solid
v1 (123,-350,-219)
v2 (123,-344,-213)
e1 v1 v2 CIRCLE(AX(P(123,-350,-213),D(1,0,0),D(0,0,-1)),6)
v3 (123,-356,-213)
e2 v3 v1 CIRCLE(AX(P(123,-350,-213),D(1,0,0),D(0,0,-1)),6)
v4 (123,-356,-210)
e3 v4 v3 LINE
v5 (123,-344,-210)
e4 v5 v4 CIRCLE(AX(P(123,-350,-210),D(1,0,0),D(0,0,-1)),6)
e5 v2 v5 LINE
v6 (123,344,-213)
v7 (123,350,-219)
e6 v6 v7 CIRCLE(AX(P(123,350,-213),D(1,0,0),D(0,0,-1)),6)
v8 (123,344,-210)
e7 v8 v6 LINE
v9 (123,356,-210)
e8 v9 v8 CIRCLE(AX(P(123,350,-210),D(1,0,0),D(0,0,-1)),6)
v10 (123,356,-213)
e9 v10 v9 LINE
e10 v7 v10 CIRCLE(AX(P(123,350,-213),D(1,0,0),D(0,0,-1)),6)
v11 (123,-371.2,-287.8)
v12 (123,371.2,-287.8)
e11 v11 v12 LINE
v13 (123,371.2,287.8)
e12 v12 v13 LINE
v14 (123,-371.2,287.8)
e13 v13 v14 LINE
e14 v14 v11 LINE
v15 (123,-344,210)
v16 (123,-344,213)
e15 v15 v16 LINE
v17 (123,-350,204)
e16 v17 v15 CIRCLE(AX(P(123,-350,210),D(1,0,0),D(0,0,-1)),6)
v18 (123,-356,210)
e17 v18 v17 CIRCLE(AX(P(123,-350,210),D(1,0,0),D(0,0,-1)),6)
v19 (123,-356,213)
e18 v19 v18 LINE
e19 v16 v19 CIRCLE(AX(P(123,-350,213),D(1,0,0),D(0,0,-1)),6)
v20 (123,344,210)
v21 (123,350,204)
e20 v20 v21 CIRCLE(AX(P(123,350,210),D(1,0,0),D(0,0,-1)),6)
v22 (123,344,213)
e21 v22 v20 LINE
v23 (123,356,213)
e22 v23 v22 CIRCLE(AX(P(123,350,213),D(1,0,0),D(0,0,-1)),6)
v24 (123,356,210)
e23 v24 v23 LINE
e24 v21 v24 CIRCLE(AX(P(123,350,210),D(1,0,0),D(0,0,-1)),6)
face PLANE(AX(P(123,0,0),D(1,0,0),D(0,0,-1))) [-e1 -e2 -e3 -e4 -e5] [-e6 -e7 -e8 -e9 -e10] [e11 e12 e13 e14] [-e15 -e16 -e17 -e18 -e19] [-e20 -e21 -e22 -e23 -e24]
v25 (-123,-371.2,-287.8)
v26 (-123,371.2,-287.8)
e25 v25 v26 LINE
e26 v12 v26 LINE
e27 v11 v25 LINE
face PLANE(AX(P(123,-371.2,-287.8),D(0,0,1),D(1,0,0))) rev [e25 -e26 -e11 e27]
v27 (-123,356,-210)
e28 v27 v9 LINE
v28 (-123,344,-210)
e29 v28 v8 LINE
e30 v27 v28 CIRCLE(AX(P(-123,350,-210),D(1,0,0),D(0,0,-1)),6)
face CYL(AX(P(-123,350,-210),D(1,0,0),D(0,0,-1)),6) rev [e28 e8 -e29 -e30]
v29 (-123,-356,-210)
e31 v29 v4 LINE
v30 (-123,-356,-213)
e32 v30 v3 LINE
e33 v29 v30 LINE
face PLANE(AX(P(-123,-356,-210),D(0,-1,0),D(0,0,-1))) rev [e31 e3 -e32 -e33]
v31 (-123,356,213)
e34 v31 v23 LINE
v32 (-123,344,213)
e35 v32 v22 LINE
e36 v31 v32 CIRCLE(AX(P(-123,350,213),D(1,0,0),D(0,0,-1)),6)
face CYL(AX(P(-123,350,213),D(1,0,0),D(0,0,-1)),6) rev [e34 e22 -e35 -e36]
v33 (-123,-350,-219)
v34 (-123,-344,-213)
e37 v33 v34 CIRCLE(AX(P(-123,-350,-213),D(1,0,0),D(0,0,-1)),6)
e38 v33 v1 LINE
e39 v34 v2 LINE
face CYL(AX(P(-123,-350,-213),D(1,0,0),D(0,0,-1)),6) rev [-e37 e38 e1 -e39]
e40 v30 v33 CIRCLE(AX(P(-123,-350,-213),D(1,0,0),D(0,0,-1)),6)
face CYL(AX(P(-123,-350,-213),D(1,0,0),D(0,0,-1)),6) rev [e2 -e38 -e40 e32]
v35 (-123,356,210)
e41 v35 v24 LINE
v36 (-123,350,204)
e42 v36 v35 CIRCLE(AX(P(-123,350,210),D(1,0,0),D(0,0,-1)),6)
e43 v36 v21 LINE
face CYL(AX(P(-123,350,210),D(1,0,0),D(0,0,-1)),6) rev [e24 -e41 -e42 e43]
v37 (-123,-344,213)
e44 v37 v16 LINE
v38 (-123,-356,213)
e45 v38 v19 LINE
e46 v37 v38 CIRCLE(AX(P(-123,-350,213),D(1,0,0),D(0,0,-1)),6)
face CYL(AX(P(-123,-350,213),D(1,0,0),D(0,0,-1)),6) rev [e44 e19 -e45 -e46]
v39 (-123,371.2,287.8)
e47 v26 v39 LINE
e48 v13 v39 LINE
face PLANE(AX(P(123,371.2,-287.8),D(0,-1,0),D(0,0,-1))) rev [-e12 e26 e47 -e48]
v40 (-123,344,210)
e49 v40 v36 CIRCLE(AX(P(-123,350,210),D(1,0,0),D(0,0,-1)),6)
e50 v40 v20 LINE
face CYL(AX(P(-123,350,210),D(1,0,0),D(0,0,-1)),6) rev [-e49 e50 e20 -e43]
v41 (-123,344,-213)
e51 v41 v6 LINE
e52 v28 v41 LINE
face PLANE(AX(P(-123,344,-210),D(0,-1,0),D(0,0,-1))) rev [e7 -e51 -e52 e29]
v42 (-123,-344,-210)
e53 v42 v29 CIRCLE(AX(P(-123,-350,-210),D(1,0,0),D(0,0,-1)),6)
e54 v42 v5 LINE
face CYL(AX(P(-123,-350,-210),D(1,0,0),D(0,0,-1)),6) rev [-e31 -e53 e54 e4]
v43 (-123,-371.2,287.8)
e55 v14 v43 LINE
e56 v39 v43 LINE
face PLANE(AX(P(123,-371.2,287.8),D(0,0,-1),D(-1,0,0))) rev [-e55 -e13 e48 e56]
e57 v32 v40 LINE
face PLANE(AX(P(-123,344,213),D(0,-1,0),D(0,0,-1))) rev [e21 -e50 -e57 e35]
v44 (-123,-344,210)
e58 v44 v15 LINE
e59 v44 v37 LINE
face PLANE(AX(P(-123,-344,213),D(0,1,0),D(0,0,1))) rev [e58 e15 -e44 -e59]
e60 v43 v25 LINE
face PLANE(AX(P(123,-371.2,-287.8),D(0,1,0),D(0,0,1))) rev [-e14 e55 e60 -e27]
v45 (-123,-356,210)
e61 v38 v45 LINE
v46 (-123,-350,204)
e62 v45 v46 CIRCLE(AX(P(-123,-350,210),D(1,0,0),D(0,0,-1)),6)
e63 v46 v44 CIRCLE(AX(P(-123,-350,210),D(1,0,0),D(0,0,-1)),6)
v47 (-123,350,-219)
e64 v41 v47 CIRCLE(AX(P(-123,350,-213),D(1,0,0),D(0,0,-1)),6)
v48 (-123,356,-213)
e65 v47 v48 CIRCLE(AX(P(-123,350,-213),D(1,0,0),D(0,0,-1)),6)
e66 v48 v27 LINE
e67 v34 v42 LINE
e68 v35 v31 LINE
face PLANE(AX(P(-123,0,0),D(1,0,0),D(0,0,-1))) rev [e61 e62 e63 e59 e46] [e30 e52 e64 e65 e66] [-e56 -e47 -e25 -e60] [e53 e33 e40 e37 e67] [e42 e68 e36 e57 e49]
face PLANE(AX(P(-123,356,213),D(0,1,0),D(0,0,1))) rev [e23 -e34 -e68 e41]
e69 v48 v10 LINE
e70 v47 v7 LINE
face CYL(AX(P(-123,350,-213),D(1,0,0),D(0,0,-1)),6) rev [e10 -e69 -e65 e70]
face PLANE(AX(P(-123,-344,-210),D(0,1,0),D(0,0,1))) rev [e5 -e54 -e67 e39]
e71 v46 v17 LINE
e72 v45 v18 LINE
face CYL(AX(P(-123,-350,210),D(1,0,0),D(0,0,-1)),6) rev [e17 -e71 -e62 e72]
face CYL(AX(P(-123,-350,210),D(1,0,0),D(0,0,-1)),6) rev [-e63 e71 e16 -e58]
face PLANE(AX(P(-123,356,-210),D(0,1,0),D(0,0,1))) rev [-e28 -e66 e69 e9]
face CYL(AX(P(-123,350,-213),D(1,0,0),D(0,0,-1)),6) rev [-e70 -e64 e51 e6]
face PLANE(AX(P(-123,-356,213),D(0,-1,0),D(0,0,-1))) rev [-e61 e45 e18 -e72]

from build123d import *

# Parameters (mm, degrees)
SKETCH_1_W          = 575.6
SKETCH_1_H          = 742.4
EXTRUDE_1_DEPTH     = 123
CUT_EXTRUDE_1_DEPTH = 531.220972803


with BuildPart() as part:
    # 草图1 → 凸台-拉伸1 (new, symmetric)
    with BuildSketch(Plane(origin=(0, 0, 0), x_dir=(0, 0, -1), z_dir=(1, 0, 0))):
        Rectangle(SKETCH_1_W, SKETCH_1_H)
    extrude(amount=EXTRUDE_1_DEPTH, both=True)

    # 草图2 → 切除-拉伸1 (cut, through all)
    with BuildSketch(Plane(origin=(123, 0, 0), x_dir=(0, 0, -1), z_dir=(1, 0, 0))):
        with BuildLine():
            Line((-213, 356), (-210, 356))
            ThreePointArc((-210, 356), (-204, 350), (-210, 344))
            Line((-210, 344), (-213, 344))
            ThreePointArc((-213, 344), (-219, 350), (-213, 356))
        make_face()
        with BuildLine():
            Line((210, 356), (213, 356))
            ThreePointArc((213, 356), (219, 350), (213, 344))
            Line((213, 344), (210, 344))
            ThreePointArc((210, 344), (204, 350), (210, 356))
        make_face()
        with BuildLine():
            Line((210, -344), (213, -344))
            ThreePointArc((213, -344), (219, -350), (213, -356))
            Line((213, -356), (210, -356))
            ThreePointArc((210, -356), (204, -350), (210, -344))
        make_face()
        with BuildLine():
            Line((-213, -344), (-210, -344))
            ThreePointArc((-210, -344), (-204, -350), (-210, -356))
            Line((-210, -356), (-213, -356))
            ThreePointArc((-213, -356), (-219, -350), (-213, -344))
        make_face()
    extrude(amount=-CUT_EXTRUDE_1_DEPTH, mode=Mode.SUBTRACT)


solid = part.part
